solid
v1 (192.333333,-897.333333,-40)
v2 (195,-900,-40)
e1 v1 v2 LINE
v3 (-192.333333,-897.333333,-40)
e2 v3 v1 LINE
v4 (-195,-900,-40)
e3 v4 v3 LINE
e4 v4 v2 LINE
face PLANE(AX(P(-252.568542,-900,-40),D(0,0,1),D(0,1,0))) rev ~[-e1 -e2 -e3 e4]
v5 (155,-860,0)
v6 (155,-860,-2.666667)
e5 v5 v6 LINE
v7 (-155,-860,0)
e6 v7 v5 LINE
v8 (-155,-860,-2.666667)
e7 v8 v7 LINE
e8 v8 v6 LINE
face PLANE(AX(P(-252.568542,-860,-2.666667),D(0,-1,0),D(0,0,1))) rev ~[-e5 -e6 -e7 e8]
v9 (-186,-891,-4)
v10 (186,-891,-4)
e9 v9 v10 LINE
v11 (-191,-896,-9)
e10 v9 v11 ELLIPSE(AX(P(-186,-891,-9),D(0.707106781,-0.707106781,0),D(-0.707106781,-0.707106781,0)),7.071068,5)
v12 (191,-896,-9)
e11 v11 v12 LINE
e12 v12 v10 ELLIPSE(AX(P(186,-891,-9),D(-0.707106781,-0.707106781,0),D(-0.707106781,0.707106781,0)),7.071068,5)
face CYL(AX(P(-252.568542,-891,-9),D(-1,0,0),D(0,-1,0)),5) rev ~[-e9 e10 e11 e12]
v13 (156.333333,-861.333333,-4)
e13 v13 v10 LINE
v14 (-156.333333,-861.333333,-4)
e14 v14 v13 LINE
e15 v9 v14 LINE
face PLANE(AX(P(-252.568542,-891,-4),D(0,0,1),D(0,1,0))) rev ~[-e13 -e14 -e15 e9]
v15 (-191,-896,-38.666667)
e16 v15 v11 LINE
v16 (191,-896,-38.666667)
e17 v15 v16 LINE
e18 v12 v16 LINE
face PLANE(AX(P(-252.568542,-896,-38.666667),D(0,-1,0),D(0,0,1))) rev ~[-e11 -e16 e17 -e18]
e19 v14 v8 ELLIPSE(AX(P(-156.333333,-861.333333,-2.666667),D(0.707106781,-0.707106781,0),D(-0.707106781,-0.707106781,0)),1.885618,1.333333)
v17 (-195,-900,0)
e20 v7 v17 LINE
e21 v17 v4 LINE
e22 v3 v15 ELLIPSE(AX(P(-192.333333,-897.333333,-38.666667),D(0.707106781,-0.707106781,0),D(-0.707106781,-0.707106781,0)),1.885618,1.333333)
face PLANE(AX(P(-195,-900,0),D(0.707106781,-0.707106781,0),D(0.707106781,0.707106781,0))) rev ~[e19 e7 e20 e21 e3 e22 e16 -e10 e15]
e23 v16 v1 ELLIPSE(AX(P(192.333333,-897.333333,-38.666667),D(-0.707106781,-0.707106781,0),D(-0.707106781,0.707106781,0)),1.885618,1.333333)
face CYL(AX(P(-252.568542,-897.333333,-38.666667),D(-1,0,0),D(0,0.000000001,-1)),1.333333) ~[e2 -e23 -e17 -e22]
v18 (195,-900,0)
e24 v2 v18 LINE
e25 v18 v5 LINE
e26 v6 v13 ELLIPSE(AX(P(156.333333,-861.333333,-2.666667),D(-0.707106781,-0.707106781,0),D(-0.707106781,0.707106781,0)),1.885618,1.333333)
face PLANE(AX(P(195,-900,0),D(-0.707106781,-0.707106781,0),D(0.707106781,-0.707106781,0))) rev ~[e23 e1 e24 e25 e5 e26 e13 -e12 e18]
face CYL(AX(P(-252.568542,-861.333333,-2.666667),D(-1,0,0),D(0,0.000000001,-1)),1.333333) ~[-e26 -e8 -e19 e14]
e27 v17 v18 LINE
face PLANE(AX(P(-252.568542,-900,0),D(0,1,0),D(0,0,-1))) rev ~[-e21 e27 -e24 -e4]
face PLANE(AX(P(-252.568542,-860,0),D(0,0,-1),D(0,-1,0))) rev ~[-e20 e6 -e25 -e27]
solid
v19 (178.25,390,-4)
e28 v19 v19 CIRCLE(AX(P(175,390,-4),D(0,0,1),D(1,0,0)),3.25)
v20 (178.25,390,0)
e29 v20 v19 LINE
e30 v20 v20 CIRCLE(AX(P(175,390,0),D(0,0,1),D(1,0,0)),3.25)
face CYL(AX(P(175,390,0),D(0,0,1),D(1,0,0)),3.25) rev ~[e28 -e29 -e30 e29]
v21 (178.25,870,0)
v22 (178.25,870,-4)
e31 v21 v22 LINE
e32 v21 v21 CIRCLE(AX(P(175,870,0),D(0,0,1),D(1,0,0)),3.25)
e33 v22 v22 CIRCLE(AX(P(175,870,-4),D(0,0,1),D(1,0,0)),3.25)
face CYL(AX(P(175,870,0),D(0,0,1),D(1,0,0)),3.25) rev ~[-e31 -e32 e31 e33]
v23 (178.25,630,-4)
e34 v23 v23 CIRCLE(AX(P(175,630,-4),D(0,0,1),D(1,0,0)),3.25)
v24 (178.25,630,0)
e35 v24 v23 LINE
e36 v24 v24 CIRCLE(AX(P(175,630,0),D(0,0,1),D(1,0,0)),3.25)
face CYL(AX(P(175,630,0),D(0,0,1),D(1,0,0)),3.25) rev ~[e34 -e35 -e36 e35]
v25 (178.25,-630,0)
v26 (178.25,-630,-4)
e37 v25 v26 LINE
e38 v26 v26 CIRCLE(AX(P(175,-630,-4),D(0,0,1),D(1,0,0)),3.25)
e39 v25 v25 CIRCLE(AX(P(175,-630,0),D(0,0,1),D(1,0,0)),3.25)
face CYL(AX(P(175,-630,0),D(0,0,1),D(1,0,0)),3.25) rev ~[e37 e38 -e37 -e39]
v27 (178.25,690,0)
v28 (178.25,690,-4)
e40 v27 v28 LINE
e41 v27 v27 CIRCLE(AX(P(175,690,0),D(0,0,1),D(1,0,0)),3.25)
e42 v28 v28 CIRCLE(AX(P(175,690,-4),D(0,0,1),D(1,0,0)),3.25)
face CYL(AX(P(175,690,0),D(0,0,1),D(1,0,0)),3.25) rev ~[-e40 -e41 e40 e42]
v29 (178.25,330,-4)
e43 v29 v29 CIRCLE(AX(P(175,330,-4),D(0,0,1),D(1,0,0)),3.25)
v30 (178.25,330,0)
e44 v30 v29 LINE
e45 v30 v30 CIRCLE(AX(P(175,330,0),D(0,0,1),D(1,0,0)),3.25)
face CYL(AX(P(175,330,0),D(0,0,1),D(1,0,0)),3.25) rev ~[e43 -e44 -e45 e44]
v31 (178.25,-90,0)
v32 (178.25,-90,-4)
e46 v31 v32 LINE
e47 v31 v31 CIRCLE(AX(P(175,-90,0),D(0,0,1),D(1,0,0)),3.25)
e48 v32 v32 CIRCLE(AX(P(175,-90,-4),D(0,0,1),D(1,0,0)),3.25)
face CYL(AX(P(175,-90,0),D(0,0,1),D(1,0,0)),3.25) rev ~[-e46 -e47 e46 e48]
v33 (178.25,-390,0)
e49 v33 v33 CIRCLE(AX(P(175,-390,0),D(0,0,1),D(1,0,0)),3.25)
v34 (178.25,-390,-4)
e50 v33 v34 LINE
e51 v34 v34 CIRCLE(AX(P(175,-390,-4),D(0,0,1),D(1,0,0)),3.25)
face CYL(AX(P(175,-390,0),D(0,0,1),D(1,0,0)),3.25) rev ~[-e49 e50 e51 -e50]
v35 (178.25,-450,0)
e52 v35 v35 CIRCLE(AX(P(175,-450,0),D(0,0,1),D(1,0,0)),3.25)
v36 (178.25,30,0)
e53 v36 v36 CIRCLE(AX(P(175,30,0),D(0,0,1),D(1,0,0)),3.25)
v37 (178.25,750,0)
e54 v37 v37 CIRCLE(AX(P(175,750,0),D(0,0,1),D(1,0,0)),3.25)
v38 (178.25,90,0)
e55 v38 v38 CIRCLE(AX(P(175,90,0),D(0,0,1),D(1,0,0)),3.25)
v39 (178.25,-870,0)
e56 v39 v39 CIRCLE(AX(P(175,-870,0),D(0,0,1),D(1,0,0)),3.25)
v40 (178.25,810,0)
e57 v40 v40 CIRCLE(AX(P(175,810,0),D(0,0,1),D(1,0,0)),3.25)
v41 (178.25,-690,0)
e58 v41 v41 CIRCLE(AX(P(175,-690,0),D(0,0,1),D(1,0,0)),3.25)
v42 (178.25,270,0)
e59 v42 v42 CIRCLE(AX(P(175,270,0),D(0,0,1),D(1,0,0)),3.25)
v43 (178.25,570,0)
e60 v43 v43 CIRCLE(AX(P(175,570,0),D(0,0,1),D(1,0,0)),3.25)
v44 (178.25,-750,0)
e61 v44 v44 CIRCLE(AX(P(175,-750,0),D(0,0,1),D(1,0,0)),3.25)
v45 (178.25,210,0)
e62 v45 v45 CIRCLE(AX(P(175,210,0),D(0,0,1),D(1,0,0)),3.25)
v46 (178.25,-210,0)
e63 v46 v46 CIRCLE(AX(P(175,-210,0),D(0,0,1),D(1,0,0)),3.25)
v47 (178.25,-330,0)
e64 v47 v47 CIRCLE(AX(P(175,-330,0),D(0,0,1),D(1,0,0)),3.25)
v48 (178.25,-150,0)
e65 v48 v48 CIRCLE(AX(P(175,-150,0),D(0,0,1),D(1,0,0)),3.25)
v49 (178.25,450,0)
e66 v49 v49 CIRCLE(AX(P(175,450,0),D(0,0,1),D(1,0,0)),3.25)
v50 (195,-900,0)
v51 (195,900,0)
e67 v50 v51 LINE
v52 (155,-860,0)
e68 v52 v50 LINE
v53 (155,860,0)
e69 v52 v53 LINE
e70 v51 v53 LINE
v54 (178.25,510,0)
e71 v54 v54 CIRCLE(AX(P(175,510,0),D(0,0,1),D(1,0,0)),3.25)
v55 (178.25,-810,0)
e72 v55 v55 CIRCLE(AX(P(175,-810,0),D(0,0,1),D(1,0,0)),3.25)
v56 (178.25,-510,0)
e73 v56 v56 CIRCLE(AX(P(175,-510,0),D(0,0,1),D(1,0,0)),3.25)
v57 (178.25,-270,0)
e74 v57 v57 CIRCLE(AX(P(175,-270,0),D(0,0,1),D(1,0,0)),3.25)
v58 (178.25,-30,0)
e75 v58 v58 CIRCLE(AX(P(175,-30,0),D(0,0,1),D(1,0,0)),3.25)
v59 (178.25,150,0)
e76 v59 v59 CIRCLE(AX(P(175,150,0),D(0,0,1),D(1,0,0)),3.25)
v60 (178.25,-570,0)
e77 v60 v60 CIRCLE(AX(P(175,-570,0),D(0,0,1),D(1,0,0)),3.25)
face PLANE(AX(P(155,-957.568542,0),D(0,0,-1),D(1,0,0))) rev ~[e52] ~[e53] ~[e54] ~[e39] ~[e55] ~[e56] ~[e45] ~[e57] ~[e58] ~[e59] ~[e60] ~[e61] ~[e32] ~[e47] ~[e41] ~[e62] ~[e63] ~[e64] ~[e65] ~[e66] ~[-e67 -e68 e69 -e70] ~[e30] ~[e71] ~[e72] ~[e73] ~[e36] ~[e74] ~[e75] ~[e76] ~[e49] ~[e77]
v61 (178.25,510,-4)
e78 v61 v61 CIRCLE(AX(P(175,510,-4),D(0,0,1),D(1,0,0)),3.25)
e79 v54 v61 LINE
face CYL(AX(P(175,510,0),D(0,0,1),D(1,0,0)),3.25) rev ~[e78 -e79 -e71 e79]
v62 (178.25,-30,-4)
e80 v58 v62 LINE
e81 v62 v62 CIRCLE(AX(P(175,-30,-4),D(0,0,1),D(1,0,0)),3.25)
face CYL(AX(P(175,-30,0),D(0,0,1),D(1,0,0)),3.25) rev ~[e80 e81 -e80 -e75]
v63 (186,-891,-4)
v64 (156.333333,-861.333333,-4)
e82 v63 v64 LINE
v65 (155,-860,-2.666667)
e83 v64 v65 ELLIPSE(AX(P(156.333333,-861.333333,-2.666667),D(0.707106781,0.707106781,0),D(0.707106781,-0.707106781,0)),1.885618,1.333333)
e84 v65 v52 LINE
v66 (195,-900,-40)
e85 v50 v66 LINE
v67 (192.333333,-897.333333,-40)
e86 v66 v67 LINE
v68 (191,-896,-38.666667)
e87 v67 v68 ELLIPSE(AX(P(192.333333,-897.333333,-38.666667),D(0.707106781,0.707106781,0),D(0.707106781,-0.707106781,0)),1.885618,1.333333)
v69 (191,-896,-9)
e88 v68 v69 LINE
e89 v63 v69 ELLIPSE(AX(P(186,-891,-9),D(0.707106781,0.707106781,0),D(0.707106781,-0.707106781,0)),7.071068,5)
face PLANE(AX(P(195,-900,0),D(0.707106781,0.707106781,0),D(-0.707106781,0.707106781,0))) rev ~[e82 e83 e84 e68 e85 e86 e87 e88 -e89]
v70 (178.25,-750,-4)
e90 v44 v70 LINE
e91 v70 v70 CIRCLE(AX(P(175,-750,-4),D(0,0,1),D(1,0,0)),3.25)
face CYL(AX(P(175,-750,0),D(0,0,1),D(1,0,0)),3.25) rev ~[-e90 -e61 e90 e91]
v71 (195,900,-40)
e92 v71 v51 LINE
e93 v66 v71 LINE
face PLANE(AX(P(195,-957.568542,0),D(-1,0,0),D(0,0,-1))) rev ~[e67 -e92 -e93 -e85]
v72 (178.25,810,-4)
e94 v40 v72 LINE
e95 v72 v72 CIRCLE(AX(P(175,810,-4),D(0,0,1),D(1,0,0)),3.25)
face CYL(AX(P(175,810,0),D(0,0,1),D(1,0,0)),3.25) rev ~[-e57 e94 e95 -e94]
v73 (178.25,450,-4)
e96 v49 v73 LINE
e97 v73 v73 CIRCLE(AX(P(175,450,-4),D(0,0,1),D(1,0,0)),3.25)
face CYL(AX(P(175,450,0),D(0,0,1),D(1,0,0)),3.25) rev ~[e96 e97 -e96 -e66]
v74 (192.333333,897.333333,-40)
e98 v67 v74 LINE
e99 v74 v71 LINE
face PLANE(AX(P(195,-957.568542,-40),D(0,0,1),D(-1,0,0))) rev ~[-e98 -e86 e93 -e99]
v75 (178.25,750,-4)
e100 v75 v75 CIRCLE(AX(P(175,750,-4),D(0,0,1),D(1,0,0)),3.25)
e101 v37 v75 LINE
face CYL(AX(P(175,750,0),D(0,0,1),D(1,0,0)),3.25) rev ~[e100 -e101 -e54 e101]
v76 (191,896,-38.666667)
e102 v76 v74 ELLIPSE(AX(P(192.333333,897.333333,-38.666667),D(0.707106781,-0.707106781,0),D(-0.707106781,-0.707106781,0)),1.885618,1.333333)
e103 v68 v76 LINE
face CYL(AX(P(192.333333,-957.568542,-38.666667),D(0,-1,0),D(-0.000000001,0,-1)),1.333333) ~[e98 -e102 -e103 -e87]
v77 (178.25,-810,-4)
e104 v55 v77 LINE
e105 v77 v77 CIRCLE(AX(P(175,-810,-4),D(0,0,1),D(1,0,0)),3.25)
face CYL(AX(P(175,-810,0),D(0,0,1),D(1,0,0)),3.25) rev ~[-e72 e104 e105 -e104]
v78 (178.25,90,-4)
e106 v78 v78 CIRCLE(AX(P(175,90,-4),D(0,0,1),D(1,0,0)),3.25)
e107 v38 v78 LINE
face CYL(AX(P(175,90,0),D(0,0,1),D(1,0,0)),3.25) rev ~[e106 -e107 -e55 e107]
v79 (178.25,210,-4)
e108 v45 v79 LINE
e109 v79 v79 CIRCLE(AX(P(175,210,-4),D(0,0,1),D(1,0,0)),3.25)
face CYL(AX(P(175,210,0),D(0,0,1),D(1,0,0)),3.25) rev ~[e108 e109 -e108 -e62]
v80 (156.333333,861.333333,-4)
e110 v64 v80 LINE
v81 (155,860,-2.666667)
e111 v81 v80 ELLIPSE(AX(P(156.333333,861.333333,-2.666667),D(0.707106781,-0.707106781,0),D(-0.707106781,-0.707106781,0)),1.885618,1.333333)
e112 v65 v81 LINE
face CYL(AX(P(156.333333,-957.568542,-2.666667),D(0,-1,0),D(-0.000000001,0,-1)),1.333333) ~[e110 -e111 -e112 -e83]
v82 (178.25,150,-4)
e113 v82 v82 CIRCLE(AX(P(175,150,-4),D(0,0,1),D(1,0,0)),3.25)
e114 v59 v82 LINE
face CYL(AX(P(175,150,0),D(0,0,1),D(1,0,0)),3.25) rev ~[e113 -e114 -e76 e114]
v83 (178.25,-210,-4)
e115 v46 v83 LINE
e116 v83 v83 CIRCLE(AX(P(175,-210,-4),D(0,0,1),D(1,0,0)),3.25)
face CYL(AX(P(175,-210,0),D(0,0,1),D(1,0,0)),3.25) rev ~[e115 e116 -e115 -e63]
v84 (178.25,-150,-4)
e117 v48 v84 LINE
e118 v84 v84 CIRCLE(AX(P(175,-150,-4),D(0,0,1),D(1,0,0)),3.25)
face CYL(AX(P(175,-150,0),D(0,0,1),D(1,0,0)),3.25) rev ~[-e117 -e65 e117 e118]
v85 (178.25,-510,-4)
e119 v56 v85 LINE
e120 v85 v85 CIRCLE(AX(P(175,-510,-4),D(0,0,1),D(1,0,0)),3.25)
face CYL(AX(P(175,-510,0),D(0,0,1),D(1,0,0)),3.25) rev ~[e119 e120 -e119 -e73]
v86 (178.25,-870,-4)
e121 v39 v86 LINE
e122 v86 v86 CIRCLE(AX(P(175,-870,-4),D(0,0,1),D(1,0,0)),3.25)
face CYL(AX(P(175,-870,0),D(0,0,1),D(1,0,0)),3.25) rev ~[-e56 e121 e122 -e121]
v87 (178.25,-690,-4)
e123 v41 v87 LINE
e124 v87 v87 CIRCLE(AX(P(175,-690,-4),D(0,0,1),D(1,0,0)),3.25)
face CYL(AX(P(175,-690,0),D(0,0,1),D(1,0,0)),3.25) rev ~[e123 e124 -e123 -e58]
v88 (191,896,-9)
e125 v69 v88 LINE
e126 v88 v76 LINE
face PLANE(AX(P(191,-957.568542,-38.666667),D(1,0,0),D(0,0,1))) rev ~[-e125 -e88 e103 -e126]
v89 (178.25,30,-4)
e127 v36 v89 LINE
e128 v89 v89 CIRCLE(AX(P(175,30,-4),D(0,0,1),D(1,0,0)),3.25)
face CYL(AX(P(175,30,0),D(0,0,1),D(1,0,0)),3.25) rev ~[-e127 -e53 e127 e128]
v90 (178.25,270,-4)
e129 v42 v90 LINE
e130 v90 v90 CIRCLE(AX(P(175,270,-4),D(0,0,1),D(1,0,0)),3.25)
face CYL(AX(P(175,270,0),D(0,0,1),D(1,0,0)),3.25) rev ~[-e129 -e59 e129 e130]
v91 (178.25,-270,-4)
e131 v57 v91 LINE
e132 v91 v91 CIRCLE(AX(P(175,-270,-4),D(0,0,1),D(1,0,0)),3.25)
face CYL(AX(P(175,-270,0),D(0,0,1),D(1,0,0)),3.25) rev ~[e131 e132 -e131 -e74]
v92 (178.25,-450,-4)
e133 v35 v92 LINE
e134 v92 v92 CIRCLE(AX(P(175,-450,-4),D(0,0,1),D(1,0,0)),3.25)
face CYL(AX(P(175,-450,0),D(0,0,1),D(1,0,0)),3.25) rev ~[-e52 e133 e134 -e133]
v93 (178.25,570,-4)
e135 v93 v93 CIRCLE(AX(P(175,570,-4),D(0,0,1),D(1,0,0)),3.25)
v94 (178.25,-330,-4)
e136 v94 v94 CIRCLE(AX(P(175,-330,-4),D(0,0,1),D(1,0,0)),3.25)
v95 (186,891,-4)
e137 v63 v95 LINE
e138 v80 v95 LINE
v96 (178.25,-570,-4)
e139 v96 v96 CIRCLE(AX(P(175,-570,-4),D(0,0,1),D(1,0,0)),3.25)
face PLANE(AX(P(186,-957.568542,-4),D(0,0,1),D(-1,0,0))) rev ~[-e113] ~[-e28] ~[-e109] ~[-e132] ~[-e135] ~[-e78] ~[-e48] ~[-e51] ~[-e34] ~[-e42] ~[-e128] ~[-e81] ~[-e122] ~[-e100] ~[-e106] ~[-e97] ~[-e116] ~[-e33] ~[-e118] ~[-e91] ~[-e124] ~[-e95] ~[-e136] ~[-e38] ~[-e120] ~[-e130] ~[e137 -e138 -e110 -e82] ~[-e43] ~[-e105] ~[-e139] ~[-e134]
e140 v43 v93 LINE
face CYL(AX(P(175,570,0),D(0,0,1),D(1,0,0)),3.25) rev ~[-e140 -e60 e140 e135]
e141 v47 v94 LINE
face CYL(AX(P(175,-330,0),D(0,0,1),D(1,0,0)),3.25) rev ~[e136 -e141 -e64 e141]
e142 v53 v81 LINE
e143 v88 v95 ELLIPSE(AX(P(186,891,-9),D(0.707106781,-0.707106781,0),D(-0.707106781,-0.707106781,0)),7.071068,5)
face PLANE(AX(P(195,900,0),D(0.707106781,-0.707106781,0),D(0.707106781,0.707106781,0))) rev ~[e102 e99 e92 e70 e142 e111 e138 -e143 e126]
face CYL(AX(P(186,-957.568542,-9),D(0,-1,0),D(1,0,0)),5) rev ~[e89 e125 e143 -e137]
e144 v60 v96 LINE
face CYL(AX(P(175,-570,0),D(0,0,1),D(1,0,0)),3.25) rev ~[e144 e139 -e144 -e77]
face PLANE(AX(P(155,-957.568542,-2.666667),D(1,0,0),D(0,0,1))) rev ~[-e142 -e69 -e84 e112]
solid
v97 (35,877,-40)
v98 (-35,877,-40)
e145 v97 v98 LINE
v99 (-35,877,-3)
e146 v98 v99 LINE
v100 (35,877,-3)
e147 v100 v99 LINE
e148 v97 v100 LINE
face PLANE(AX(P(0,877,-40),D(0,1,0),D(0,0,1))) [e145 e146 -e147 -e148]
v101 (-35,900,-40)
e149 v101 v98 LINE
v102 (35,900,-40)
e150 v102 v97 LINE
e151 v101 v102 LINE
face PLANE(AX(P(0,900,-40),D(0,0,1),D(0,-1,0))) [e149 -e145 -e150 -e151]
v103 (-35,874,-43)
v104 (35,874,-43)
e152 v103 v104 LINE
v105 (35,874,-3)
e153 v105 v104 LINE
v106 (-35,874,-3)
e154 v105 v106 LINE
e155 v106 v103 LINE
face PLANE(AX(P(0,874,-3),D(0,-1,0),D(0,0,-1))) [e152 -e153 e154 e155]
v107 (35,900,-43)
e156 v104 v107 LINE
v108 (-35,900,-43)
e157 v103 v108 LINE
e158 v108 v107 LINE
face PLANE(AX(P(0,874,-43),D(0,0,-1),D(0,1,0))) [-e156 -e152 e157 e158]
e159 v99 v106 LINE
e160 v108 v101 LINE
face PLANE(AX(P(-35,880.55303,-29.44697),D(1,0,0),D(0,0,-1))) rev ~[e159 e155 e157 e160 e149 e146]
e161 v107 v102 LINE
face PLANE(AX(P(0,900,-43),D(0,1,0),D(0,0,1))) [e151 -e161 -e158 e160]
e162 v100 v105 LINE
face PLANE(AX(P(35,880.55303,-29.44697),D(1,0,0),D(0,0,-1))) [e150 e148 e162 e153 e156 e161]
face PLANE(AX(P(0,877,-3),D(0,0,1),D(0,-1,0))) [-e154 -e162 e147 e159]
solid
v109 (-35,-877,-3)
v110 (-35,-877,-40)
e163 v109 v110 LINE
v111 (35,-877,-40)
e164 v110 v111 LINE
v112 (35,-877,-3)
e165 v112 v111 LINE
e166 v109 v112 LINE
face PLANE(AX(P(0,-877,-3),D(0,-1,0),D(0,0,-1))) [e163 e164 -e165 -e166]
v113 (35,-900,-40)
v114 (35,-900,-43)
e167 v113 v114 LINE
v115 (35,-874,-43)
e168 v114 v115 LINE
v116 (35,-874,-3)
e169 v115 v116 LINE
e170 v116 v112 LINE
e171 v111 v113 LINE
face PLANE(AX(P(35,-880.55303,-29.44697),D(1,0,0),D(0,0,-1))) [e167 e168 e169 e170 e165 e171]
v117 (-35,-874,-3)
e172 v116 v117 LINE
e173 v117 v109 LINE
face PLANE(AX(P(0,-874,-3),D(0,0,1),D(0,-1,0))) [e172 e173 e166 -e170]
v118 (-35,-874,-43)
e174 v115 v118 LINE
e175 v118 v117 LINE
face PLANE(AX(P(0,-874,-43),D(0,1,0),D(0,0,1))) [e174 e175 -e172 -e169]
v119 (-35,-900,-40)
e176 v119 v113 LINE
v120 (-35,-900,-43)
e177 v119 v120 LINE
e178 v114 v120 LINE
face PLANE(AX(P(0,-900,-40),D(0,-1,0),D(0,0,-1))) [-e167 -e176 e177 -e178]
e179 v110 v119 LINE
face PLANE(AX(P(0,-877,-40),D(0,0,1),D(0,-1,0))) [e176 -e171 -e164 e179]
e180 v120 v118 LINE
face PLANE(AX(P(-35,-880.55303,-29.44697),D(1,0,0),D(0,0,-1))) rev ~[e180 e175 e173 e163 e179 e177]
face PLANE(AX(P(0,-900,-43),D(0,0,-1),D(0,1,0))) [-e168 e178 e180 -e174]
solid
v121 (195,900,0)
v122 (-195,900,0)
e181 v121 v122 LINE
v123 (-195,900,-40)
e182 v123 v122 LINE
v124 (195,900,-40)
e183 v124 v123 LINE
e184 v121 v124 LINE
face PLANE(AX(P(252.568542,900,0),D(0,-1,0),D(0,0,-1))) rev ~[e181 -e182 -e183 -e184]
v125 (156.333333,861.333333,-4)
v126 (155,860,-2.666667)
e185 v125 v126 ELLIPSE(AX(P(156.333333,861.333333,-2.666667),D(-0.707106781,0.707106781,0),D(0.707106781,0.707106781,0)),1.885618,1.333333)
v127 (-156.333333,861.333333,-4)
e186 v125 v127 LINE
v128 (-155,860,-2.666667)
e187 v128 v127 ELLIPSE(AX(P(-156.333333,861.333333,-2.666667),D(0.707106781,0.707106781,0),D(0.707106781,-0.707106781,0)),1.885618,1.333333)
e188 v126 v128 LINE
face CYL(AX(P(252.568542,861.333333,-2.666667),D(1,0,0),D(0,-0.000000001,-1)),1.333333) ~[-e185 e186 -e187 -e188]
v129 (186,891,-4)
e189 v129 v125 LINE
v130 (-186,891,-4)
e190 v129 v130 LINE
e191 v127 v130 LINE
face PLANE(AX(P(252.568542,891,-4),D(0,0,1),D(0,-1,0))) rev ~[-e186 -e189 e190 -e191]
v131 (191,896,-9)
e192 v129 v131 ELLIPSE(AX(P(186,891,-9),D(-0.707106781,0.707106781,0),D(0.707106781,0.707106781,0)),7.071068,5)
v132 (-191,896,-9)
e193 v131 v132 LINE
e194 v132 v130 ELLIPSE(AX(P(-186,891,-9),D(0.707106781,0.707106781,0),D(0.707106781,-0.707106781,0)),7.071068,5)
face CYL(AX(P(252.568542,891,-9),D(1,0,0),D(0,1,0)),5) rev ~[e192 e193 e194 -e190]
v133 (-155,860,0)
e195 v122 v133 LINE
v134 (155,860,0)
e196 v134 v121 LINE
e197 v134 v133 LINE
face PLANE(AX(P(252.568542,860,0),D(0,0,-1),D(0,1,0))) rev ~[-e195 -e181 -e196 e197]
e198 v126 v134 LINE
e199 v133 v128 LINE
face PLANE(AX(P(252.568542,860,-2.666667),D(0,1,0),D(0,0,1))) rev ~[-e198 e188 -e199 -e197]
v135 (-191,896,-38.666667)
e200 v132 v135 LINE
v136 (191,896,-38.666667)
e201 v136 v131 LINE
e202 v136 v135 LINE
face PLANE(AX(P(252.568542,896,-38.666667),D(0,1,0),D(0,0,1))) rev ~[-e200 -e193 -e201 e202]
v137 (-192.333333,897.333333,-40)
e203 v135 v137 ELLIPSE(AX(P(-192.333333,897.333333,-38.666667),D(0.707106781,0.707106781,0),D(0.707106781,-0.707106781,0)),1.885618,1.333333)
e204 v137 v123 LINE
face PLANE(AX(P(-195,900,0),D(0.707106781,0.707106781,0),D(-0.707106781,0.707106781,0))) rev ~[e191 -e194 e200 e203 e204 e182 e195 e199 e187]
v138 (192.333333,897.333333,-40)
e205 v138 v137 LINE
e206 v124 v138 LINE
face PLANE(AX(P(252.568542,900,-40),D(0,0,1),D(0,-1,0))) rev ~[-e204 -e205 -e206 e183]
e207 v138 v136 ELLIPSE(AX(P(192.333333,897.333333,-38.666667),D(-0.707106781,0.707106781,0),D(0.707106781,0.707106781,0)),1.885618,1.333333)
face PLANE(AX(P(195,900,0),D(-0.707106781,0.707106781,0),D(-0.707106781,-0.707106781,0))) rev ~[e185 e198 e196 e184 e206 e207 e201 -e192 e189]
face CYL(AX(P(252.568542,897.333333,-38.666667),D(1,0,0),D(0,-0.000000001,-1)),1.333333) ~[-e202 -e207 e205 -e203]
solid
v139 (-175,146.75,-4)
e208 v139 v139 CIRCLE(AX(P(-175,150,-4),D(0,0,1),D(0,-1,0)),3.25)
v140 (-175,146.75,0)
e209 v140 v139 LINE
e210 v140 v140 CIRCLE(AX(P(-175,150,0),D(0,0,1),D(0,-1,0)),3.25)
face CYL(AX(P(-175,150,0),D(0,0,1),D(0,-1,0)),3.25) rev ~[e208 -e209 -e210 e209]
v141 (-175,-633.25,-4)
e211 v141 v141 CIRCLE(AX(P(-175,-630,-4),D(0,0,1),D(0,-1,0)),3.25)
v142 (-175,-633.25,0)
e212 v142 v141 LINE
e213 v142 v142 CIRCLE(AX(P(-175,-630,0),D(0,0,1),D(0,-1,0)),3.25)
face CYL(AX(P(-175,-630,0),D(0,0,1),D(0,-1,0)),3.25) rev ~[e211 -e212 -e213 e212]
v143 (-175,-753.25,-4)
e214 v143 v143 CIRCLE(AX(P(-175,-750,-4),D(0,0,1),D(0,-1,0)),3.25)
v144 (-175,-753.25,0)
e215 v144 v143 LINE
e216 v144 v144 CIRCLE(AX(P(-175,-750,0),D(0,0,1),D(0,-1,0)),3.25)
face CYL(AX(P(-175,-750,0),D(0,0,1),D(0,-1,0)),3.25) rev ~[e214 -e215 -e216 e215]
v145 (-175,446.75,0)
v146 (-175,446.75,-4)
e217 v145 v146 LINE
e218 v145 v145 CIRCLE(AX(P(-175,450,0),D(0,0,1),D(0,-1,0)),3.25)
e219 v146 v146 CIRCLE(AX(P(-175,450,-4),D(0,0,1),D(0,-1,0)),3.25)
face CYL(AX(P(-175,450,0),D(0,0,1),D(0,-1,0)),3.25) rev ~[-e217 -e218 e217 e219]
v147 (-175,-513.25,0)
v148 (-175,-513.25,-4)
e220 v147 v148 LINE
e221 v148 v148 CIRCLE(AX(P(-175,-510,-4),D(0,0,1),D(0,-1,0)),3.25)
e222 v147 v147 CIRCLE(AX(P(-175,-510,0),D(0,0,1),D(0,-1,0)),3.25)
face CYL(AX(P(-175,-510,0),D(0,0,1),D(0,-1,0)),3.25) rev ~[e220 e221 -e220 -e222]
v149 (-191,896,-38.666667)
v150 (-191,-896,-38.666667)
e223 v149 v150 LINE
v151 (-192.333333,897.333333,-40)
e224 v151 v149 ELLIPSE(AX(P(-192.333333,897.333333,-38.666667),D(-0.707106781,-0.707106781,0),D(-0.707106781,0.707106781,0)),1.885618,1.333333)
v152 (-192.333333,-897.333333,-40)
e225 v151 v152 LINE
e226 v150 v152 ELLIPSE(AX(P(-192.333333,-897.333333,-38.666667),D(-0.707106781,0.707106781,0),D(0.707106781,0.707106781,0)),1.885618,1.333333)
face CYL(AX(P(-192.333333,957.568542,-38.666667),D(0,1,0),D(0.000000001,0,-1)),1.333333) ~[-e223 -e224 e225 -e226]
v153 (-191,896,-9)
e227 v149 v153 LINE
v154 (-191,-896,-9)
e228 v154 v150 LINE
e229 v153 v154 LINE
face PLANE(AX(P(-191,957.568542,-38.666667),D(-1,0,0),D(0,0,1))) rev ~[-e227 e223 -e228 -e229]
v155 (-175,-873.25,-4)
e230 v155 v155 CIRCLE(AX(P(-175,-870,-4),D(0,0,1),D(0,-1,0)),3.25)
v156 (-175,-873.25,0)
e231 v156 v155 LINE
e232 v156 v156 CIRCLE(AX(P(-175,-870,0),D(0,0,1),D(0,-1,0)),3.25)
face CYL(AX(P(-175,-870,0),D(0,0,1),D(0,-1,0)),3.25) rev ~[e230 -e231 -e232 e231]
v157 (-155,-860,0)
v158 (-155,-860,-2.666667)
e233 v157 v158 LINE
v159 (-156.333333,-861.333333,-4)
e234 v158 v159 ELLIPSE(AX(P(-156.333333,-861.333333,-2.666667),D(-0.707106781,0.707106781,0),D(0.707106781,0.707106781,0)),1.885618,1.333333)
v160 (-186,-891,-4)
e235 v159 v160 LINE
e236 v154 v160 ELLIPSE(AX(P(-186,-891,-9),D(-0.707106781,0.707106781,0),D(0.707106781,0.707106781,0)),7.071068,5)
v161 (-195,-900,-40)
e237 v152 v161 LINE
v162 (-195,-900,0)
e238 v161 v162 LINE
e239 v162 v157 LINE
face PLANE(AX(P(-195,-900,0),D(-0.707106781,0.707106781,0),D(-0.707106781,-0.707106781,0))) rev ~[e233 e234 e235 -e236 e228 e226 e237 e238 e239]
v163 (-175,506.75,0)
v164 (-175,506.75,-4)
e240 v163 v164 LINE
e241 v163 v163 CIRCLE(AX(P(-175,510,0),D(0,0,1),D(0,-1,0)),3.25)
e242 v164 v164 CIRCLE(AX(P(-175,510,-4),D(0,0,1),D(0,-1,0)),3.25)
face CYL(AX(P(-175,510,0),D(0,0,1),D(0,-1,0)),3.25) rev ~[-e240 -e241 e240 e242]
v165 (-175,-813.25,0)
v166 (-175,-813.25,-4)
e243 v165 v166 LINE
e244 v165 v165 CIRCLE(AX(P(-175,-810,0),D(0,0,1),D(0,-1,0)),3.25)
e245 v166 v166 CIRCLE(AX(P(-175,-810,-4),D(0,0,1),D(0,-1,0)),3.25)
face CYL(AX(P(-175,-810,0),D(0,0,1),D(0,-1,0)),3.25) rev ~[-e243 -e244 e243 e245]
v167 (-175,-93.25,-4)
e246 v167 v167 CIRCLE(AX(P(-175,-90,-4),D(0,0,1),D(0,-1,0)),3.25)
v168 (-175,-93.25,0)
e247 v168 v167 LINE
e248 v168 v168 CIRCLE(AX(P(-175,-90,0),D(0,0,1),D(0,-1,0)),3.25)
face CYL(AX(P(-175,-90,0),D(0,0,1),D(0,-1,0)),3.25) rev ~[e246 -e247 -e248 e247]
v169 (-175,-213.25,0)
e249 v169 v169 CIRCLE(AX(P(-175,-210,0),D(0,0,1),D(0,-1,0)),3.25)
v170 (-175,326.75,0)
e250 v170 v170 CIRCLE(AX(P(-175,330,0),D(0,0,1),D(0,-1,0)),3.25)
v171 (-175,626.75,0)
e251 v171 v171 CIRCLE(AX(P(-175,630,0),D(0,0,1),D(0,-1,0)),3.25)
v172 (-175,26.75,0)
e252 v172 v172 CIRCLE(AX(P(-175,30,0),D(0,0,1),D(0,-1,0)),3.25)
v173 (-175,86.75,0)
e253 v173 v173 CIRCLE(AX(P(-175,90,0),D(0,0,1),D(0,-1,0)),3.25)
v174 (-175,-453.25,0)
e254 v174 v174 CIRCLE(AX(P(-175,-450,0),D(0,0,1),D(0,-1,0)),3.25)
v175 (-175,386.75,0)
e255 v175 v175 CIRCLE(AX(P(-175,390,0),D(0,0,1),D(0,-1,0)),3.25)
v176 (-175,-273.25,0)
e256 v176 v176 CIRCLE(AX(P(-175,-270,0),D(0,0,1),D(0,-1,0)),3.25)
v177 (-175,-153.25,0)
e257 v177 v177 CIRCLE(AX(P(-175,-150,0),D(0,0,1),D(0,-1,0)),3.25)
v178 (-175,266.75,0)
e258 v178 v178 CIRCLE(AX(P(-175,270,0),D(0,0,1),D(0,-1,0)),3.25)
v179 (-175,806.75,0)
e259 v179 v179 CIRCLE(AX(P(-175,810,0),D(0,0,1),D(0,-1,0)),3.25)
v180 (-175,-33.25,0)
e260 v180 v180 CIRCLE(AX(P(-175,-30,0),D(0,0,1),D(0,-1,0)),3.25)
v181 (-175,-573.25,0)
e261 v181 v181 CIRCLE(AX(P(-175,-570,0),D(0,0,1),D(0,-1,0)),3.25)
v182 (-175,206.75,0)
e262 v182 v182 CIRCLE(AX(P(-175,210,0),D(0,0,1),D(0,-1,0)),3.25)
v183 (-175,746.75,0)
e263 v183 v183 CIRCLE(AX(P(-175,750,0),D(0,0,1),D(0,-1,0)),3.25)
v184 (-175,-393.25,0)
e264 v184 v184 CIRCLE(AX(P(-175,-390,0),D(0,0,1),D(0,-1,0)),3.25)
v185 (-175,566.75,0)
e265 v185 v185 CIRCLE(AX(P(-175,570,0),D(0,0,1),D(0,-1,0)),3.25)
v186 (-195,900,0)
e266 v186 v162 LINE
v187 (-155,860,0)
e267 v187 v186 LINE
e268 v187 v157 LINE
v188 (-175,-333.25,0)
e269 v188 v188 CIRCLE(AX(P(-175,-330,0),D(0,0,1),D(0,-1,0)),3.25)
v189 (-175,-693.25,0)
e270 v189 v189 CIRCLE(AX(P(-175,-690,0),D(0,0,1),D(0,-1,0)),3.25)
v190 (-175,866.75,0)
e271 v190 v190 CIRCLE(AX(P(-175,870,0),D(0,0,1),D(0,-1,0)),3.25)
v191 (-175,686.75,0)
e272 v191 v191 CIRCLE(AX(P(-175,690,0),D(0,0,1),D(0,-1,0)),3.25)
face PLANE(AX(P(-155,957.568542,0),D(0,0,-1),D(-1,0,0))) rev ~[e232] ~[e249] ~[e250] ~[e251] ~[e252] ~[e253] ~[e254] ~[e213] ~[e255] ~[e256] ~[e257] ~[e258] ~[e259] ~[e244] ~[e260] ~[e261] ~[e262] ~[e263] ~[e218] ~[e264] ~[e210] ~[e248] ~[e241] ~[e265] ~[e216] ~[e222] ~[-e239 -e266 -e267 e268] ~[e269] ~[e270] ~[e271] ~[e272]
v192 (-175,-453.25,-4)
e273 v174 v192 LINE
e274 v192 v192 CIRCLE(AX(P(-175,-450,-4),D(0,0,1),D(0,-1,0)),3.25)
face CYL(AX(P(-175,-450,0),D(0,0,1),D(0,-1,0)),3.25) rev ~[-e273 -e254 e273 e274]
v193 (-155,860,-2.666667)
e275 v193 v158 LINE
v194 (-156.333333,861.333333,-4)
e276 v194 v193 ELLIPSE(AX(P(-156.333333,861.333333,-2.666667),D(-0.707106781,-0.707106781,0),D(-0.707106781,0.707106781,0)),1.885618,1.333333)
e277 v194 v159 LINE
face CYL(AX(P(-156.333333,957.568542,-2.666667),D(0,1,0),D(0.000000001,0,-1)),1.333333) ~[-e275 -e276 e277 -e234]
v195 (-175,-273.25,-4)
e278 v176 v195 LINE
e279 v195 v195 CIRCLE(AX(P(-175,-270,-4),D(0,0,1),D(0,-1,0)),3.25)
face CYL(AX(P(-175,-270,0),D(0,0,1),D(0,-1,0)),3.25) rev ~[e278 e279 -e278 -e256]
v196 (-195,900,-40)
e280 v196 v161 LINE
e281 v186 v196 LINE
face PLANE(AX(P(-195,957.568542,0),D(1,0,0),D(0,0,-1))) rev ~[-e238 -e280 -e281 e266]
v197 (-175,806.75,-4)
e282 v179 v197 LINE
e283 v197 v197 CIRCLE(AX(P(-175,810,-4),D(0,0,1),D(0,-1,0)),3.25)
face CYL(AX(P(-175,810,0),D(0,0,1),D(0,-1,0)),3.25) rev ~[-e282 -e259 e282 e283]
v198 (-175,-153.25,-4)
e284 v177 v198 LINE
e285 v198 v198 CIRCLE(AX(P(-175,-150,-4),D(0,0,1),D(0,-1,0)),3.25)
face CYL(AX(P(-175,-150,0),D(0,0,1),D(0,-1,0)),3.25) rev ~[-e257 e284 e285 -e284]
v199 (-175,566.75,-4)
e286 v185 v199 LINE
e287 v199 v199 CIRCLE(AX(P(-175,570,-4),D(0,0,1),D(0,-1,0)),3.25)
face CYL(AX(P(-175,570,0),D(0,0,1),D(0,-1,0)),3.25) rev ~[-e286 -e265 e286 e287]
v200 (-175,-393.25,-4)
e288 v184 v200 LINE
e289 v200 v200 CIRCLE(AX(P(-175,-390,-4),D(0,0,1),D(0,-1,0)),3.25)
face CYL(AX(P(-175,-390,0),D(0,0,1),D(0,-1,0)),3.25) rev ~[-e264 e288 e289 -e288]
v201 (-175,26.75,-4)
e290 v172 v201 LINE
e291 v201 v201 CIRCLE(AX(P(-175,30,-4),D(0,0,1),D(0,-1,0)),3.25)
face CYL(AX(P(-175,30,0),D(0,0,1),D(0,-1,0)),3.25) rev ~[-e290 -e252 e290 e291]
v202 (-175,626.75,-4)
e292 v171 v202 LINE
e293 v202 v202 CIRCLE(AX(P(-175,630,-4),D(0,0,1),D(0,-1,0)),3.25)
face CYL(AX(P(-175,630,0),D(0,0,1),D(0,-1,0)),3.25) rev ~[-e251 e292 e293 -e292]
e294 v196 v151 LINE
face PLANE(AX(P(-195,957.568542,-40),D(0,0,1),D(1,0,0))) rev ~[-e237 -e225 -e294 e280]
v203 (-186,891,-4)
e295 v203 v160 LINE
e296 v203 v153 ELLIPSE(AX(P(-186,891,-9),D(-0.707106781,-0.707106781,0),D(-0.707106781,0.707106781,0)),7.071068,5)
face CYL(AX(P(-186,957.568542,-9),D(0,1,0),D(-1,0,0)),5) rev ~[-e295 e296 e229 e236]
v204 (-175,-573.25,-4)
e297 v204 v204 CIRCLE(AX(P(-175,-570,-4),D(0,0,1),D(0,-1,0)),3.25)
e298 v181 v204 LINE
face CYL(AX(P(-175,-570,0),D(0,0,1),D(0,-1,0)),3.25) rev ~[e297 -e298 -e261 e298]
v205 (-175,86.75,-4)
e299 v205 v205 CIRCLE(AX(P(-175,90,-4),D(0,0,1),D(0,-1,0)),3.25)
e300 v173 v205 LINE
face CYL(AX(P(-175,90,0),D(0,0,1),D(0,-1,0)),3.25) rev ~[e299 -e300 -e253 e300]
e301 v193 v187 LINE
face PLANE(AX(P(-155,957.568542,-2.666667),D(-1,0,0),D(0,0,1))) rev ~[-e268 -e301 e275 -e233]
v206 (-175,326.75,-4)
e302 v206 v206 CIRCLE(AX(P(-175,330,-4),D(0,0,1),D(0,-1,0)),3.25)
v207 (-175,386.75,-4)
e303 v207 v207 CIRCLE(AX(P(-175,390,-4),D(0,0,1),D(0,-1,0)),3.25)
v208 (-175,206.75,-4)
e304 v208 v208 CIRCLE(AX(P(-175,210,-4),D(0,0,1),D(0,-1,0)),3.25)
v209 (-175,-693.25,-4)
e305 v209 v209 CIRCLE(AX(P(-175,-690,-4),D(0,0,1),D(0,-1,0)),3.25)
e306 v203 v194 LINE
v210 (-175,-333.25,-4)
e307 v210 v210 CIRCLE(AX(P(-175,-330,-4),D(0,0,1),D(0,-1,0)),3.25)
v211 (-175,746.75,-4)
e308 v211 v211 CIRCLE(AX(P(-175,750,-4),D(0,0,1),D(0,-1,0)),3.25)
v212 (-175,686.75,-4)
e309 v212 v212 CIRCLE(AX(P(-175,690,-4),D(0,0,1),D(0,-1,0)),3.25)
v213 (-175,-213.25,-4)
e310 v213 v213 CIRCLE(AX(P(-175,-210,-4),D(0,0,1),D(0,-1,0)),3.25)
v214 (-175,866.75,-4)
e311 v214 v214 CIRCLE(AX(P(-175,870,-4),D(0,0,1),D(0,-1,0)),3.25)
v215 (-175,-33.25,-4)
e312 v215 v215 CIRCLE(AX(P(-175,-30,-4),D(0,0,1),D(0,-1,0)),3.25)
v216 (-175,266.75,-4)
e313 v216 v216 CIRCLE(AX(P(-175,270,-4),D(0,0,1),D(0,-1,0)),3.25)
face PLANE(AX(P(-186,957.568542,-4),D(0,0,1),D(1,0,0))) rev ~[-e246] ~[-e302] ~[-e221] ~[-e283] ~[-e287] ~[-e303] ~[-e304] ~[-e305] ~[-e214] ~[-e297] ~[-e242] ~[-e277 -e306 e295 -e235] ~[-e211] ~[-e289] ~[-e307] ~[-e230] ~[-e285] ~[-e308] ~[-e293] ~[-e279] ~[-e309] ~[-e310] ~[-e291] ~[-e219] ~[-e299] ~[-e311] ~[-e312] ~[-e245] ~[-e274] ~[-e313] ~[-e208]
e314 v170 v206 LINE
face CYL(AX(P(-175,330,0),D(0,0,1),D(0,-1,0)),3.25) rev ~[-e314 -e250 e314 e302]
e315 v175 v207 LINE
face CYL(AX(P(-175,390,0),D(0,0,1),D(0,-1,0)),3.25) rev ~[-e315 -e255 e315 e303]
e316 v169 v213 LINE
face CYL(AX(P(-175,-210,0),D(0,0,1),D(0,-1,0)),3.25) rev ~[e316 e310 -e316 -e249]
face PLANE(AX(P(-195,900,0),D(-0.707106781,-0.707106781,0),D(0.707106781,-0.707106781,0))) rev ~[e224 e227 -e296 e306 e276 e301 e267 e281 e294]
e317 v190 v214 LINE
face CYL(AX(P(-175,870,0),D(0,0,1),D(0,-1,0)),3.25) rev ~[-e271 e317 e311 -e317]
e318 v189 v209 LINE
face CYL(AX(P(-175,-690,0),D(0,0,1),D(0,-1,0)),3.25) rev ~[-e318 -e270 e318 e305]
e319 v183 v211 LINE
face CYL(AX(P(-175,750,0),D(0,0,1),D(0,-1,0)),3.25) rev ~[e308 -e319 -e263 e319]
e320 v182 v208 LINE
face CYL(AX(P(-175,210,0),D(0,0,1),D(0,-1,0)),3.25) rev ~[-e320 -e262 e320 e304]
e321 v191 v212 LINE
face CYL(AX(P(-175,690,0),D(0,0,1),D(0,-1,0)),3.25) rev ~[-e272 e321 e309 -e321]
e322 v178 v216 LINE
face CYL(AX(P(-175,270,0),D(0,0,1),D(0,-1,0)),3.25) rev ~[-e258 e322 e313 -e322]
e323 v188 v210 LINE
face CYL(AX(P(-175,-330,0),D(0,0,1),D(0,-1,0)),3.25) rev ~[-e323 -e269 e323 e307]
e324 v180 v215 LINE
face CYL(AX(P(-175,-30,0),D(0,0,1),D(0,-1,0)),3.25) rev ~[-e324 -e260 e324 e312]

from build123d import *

# Parameters (mm, degrees)
MEMBER_1_DEPTH      = 1857.568542495
MEMBER_1_DEPTH_BACK = 57.568542495
MEMBER_1_2_DEPTH    = 505.13708499
MEMBER_1_3_DEPTH    = 1915.13708499
MEMBER_1_4_DEPTH    = 505.13708499
SKETCH_2_R          = 3.25
CUT_EXTRUDE_1_DEPTH = 4
EXTRUDE_1_DEPTH     = 35
EXTRUDE_1_2_DEPTH   = 35


with BuildPart() as part:
    # Sketch1 → Member 1 (new, two sides: drawn at the far end of the back side and taken through both)
    with BuildSketch(Plane(origin=(195, -900, 0), x_dir=(-1, 0, 0), z_dir=(0, 1, 0)).offset(-MEMBER_1_DEPTH_BACK)):
        with BuildLine():
            Line((40, 0), (0, 0))
            Line((0, 0), (0, -40))
            Line((0, -40), (2.666666667, -40))
            ThreePointArc((2.666666667, -40), (3.609475708, -39.609475708), (4, -38.666666667))
            Line((4, -38.666666667), (4, -9))
            ThreePointArc((4, -9), (5.464466094, -5.464466094), (9, -4))
            Line((9, -4), (38.666666667, -4))
            ThreePointArc((38.666666667, -4), (39.609475708, -3.609475708), (40, -2.666666667))
            Line((40, -2.666666667), (40, 0))
        make_face()
    extrude(amount=MEMBER_1_DEPTH + MEMBER_1_DEPTH_BACK)

    # Member 1 mitre 1
    split(bisect_by=Plane(origin=(195, -900, 0), x_dir=(-0.707106781, 0.707106781, 0), z_dir=(0.707106781, 0.707106781, 0)), keep=Keep.TOP)

    # Member 1 mitre 2
    split(bisect_by=Plane(origin=(195, 900, 0), x_dir=(0.707106781, 0.707106781, 0), z_dir=(0.707106781, -0.707106781, 0)), keep=Keep.TOP)


with BuildPart() as body_2:
    # Sketch1 on segment 2 (carried to segment 2) → Member 1 2 (new body)
    with BuildSketch(Plane(origin=(252.568542495, 900, 0), x_dir=(0, -1, 0), z_dir=(-1, 0, 0))):
        with BuildLine():
            Line((40, 0), (0, 0))
            Line((0, 0), (0, -40))
            Line((0, -40), (2.666666667, -40))
            ThreePointArc((2.666666667, -40), (3.609475708, -39.609475708), (4, -38.666666667))
            Line((4, -38.666666667), (4, -9))
            ThreePointArc((4, -9), (5.464466094, -5.464466094), (9, -4))
            Line((9, -4), (38.666666667, -4))
            ThreePointArc((38.666666667, -4), (39.609475708, -3.609475708), (40, -2.666666667))
            Line((40, -2.666666667), (40, 0))
        make_face()
    extrude(amount=MEMBER_1_2_DEPTH)

    # Member 1 2 mitre 1
    split(bisect_by=Plane(origin=(195, 900, 0), x_dir=(-0.707106781, -0.707106781, 0), z_dir=(-0.707106781, 0.707106781, 0)), keep=Keep.TOP)

    # Member 1 2 mitre 2
    split(bisect_by=Plane(origin=(-195, 900, 0), x_dir=(-0.707106781, 0.707106781, 0), z_dir=(0.707106781, 0.707106781, 0)), keep=Keep.TOP)


with BuildPart() as body_3:
    # Sketch1 on segment 3 (carried to segment 3) → Member 1 3 (new body)
    with BuildSketch(Plane(origin=(-195, 957.568542495, 0), x_dir=(1, 0, 0), z_dir=(0, -1, 0))):
        with BuildLine():
            Line((40, 0), (0, 0))
            Line((0, 0), (0, -40))
            Line((0, -40), (2.666666667, -40))
            ThreePointArc((2.666666667, -40), (3.609475708, -39.609475708), (4, -38.666666667))
            Line((4, -38.666666667), (4, -9))
            ThreePointArc((4, -9), (5.464466094, -5.464466094), (9, -4))
            Line((9, -4), (38.666666667, -4))
            ThreePointArc((38.666666667, -4), (39.609475708, -3.609475708), (40, -2.666666667))
            Line((40, -2.666666667), (40, 0))
        make_face()
    extrude(amount=MEMBER_1_3_DEPTH)

    # Member 1 3 mitre 1
    split(bisect_by=Plane(origin=(-195, -900, 0), x_dir=(-0.707106781, -0.707106781, 0), z_dir=(-0.707106781, 0.707106781, 0)), keep=Keep.TOP)

    # Member 1 3 mitre 2
    split(bisect_by=Plane(origin=(-195, 900, 0), x_dir=(0.707106781, -0.707106781, 0), z_dir=(-0.707106781, -0.707106781, 0)), keep=Keep.TOP)


with BuildPart() as body_4:
    # Sketch1 on segment 4 (carried to segment 4) → Member 1 4 (new body)
    with BuildSketch(Plane(origin=(-252.568542495, -900, 0), x_dir=(0, 1, 0), z_dir=(1, 0, 0))):
        with BuildLine():
            Line((40, 0), (0, 0))
            Line((0, 0), (0, -40))
            Line((0, -40), (2.666666667, -40))
            ThreePointArc((2.666666667, -40), (3.609475708, -39.609475708), (4, -38.666666667))
            Line((4, -38.666666667), (4, -9))
            ThreePointArc((4, -9), (5.464466094, -5.464466094), (9, -4))
            Line((9, -4), (38.666666667, -4))
            ThreePointArc((38.666666667, -4), (39.609475708, -3.609475708), (40, -2.666666667))
            Line((40, -2.666666667), (40, 0))
        make_face()
    extrude(amount=MEMBER_1_4_DEPTH)

    # Member 1 4 mitre 1
    split(bisect_by=Plane(origin=(195, -900, 0), x_dir=(0.707106781, -0.707106781, 0), z_dir=(-0.707106781, -0.707106781, 0)), keep=Keep.TOP)

    # Member 1 4 mitre 2
    split(bisect_by=Plane(origin=(-195, -900, 0), x_dir=(0.707106781, 0.707106781, 0), z_dir=(0.707106781, -0.707106781, 0)), keep=Keep.TOP)


with BuildPart() as cut_extrude_1_tool:
    # 草图2 → 切除-拉伸1 (new body)
    with BuildSketch(Plane.XY):
        with Locations((175, 870)):
            Circle(SKETCH_2_R)
        with Locations(Location((-175, 870, 0), (0, 0, 270))):
            Circle(SKETCH_2_R)
        with Locations(Location((-175, 810, 0), (0, 0, 270))):
            Circle(SKETCH_2_R)
        with Locations((175, 810)):
            Circle(SKETCH_2_R)
        with Locations(Location((-175, 750, 0), (0, 0, 270))):
            Circle(SKETCH_2_R)
        with Locations((175, 750)):
            Circle(SKETCH_2_R)
        with Locations(Location((-175, 690, 0), (0, 0, 270))):
            Circle(SKETCH_2_R)
        with Locations((175, 690)):
            Circle(SKETCH_2_R)
        with Locations(Location((-175, 630, 0), (0, 0, 270))):
            Circle(SKETCH_2_R)
        with Locations((175, 630)):
            Circle(SKETCH_2_R)
        with Locations(Location((-175, 570, 0), (0, 0, 270))):
            Circle(SKETCH_2_R)
        with Locations((175, 570)):
            Circle(SKETCH_2_R)
        with Locations(Location((-175, 510, 0), (0, 0, 270))):
            Circle(SKETCH_2_R)
        with Locations((175, 510)):
            Circle(SKETCH_2_R)
        with Locations(Location((-175, 450, 0), (0, 0, 270))):
            Circle(SKETCH_2_R)
        with Locations((175, 450)):
            Circle(SKETCH_2_R)
        with Locations(Location((-175, 390, 0), (0, 0, 270))):
            Circle(SKETCH_2_R)
        with Locations((175, 390)):
            Circle(SKETCH_2_R)
        with Locations(Location((-175, 330, 0), (0, 0, 270))):
            Circle(SKETCH_2_R)
        with Locations((175, 330)):
            Circle(SKETCH_2_R)
        with Locations(Location((-175, 270, 0), (0, 0, 270))):
            Circle(SKETCH_2_R)
        with Locations((175, 270)):
            Circle(SKETCH_2_R)
        with Locations(Location((-175, 210, 0), (0, 0, 270))):
            Circle(SKETCH_2_R)
        with Locations((175, 210)):
            Circle(SKETCH_2_R)
        with Locations(Location((-175, 150, 0), (0, 0, 270))):
            Circle(SKETCH_2_R)
        with Locations((175, 150)):
            Circle(SKETCH_2_R)
        with Locations(Location((-175, 90, 0), (0, 0, 270))):
            Circle(SKETCH_2_R)
        with Locations((175, 90)):
            Circle(SKETCH_2_R)
        with Locations(Location((-175, 30, 0), (0, 0, 270))):
            Circle(SKETCH_2_R)
        with Locations((175, 30)):
            Circle(SKETCH_2_R)
        with Locations(Location((-175, -30, 0), (0, 0, 270))):
            Circle(SKETCH_2_R)
        with Locations((175, -30)):
            Circle(SKETCH_2_R)
        with Locations(Location((-175, -90, 0), (0, 0, 270))):
            Circle(SKETCH_2_R)
        with Locations((175, -90)):
            Circle(SKETCH_2_R)
        with Locations(Location((-175, -150, 0), (0, 0, 270))):
            Circle(SKETCH_2_R)
        with Locations((175, -150)):
            Circle(SKETCH_2_R)
        with Locations(Location((-175, -210, 0), (0, 0, 270))):
            Circle(SKETCH_2_R)
        with Locations((175, -210)):
            Circle(SKETCH_2_R)
        with Locations(Location((-175, -270, 0), (0, 0, 270))):
            Circle(SKETCH_2_R)
        with Locations((175, -270)):
            Circle(SKETCH_2_R)
        with Locations(Location((-175, -330, 0), (0, 0, 270))):
            Circle(SKETCH_2_R)
        with Locations((175, -330)):
            Circle(SKETCH_2_R)
        with Locations(Location((-175, -390, 0), (0, 0, 270))):
            Circle(SKETCH_2_R)
        with Locations((175, -390)):
            Circle(SKETCH_2_R)
        with Locations(Location((-175, -450, 0), (0, 0, 270))):
            Circle(SKETCH_2_R)
        with Locations((175, -450)):
            Circle(SKETCH_2_R)
        with Locations(Location((-175, -510, 0), (0, 0, 270))):
            Circle(SKETCH_2_R)
        with Locations((175, -510)):
            Circle(SKETCH_2_R)
        with Locations(Location((-175, -570, 0), (0, 0, 270))):
            Circle(SKETCH_2_R)
        with Locations((175, -570)):
            Circle(SKETCH_2_R)
        with Locations(Location((-175, -630, 0), (0, 0, 270))):
            Circle(SKETCH_2_R)
        with Locations((175, -630)):
            Circle(SKETCH_2_R)
        with Locations(Location((-175, -690, 0), (0, 0, 270))):
            Circle(SKETCH_2_R)
        with Locations((175, -690)):
            Circle(SKETCH_2_R)
        with Locations(Location((-175, -750, 0), (0, 0, 270))):
            Circle(SKETCH_2_R)
        with Locations((175, -750)):
            Circle(SKETCH_2_R)
        with Locations(Location((-175, -810, 0), (0, 0, 270))):
            Circle(SKETCH_2_R)
        with Locations((175, -810)):
            Circle(SKETCH_2_R)
        with Locations(Location((-175, -870, 0), (0, 0, 270))):
            Circle(SKETCH_2_R)
        with Locations((175, -870)):
            Circle(SKETCH_2_R)
    extrude(amount=-CUT_EXTRUDE_1_DEPTH)


with BuildPart() as part_1:
    add(part.part)

    # 切除-拉伸1: cut by cut_extrude_1_tool
    add(cut_extrude_1_tool.part, mode=Mode.SUBTRACT)


with BuildPart() as body_3_1:
    add(body_3.part)

    # 切除-拉伸1: cut by cut_extrude_1_tool
    add(cut_extrude_1_tool.part, mode=Mode.SUBTRACT)


with BuildPart() as body_5:
    # 草图3 → 凸台-拉伸1 (new, symmetric)
    with BuildSketch(Plane(origin=(0, 0, 0), x_dir=(0, 0, -1), z_dir=(1, 0, 0))):
        Polygon((3, -874), (3, -877), (40, -877), (40, -900), (43, -900), (43, -874), align=None)
    extrude(amount=EXTRUDE_1_DEPTH, both=True)


with BuildPart() as body_6:
    # 草图3 → Extrude 1 2 (new, symmetric)
    with BuildSketch(Plane(origin=(0, 0, 0), x_dir=(0, 0, -1), z_dir=(1, 0, 0))):
        Polygon((3, 874), (43, 874), (43, 900), (40, 900), (40, 877), (3, 877), align=None)
    extrude(amount=EXTRUDE_1_2_DEPTH, both=True)


solid = Compound([body_2.part, body_4.part, part_1.part, body_3_1.part, body_5.part, body_6.part])
